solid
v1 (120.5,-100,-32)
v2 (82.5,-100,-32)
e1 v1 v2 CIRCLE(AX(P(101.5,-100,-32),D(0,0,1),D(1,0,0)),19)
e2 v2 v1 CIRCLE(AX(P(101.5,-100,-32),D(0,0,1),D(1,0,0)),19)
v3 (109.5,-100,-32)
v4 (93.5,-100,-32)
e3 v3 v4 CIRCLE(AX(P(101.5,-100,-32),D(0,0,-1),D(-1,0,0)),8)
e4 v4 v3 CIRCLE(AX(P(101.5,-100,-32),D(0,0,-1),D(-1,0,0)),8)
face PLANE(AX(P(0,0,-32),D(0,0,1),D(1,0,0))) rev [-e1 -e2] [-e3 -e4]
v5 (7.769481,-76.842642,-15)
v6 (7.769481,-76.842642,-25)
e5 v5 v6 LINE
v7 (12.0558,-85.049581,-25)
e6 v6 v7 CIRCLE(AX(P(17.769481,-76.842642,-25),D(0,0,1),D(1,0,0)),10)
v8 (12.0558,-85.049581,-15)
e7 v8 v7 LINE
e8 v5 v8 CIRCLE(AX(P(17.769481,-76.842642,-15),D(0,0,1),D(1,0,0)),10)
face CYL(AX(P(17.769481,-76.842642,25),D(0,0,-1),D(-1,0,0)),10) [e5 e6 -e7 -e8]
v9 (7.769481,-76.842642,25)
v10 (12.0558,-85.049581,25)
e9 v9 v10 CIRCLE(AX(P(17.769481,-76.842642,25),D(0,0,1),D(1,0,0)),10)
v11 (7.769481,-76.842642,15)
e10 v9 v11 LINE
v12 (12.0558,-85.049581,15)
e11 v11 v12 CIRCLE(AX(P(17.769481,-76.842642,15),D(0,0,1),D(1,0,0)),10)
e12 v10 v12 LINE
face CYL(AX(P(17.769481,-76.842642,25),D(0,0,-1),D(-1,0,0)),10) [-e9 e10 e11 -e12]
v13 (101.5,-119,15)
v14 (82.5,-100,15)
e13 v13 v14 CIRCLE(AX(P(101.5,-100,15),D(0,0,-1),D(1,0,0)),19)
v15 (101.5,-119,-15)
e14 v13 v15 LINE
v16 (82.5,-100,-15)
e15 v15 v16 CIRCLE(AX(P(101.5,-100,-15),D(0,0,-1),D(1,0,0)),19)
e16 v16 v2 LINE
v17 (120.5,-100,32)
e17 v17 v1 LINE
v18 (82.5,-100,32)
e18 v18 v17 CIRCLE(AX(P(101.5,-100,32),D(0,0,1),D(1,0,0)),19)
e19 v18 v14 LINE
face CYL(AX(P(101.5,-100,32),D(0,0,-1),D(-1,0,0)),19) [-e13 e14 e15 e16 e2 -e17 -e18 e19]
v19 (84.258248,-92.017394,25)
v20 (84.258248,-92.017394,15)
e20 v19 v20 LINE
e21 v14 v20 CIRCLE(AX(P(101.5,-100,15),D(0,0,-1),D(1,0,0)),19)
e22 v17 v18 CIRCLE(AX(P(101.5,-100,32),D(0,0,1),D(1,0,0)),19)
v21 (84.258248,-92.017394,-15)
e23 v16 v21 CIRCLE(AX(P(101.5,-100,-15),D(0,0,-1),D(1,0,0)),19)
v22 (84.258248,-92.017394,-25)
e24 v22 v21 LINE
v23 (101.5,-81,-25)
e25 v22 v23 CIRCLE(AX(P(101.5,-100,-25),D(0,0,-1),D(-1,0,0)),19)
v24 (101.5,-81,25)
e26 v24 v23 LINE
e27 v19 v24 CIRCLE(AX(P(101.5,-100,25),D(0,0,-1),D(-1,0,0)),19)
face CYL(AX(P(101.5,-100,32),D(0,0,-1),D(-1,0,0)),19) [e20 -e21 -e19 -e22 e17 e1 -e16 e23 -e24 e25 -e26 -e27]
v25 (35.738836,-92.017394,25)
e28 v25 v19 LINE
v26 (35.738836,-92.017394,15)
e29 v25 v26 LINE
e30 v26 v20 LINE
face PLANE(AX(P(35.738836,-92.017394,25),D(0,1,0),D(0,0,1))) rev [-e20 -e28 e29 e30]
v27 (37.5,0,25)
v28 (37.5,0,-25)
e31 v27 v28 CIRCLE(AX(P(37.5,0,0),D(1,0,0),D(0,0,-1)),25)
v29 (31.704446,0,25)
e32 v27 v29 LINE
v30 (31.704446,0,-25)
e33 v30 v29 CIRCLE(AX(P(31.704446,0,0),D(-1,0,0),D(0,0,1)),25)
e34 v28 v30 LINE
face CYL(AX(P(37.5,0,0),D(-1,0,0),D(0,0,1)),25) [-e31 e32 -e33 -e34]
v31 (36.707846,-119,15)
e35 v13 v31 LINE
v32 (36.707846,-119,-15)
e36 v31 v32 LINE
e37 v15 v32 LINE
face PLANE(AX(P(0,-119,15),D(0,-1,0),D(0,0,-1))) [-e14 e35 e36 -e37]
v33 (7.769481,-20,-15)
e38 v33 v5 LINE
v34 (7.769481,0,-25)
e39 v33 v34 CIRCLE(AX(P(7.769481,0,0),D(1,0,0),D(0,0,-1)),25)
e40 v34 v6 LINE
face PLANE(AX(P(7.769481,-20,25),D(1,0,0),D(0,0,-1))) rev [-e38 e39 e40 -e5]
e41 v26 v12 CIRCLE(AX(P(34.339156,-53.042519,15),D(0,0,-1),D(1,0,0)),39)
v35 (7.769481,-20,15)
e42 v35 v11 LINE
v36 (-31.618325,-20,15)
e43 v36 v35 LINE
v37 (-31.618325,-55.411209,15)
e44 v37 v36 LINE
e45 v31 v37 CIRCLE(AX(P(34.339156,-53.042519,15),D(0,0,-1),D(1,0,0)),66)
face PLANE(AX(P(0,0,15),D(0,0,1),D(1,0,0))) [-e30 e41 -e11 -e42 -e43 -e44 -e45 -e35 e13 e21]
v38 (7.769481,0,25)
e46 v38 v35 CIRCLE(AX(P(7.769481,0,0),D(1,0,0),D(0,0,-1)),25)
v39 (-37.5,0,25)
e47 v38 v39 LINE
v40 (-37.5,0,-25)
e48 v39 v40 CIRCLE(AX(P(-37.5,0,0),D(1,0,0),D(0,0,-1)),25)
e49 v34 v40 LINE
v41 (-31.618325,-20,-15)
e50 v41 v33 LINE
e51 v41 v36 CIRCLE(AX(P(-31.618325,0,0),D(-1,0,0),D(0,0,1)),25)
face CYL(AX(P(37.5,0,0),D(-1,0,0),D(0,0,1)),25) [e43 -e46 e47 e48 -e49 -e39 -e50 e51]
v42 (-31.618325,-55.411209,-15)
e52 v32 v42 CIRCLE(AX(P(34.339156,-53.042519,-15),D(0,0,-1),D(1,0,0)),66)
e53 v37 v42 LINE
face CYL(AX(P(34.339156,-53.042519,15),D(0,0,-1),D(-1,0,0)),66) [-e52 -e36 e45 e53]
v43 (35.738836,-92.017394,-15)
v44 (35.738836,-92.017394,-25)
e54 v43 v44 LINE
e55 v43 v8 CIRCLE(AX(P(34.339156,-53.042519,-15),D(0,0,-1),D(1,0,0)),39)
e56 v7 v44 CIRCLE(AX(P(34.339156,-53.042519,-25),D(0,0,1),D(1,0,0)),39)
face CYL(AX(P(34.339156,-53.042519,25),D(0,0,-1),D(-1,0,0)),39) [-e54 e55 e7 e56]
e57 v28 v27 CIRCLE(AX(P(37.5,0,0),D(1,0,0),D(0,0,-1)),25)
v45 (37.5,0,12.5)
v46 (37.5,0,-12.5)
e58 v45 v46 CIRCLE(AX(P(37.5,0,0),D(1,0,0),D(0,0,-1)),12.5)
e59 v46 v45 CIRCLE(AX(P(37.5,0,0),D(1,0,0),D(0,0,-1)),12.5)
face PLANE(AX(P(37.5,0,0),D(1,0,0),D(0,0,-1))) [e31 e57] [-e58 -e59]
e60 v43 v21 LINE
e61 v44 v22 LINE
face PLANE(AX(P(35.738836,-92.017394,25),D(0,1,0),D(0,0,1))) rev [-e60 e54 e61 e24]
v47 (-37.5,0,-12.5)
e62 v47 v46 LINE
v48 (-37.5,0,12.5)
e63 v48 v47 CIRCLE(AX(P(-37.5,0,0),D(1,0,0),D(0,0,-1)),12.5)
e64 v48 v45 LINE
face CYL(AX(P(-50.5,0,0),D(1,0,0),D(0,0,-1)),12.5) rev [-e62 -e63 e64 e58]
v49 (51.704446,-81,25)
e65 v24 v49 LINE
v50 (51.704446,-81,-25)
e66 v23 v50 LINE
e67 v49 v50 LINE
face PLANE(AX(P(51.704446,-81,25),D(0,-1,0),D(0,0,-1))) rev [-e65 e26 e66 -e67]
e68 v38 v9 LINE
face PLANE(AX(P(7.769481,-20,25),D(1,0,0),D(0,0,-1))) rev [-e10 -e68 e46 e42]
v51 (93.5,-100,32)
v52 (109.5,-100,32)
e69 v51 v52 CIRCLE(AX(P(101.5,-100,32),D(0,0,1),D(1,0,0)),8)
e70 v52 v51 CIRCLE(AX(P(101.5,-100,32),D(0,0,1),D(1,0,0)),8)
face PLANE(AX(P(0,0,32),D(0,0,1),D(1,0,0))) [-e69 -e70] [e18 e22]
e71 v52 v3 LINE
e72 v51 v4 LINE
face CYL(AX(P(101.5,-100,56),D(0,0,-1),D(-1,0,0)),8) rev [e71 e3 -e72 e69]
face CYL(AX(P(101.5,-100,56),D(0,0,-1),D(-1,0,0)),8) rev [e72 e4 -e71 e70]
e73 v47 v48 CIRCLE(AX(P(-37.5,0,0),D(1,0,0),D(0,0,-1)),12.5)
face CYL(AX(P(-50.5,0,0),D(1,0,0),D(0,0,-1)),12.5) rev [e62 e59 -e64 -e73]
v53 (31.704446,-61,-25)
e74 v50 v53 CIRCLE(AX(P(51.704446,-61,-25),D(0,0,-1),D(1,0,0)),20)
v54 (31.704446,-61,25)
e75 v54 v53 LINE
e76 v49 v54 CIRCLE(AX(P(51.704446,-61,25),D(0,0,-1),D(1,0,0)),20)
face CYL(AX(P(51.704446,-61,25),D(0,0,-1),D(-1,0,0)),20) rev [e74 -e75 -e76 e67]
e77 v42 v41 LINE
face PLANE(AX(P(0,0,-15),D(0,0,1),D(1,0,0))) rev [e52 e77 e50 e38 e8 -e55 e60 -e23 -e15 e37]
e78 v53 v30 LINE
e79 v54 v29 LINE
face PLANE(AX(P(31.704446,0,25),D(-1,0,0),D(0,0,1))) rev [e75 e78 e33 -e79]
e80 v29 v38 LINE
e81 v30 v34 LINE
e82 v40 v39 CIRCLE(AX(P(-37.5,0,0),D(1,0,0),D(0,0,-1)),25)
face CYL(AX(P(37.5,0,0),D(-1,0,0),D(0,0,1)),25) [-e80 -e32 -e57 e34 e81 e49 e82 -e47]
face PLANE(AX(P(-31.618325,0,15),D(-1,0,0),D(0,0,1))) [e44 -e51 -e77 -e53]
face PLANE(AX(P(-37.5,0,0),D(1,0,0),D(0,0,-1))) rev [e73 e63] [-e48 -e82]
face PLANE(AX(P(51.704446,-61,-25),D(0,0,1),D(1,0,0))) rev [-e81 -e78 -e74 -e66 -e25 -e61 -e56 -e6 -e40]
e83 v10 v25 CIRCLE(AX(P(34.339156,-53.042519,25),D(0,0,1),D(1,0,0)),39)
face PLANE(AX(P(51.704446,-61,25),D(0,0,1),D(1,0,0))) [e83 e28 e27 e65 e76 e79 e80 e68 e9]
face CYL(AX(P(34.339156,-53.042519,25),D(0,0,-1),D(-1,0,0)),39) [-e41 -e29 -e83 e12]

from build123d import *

# Parameters (mm, degrees)
HUB_1_PROFILE_R       = 25
HUB_1_BOSS_75MM_DEPTH = 37.5
HUB_2_PROFILE_R       = 19
HUB_2_BOSS_64MM_DEPTH = 32
CURVED_ARM_WEB_DEPTH  = 15
ARM_FLANGE_DEPTH      = 25
HUB_1_BORE_PROFILE_R  = 12.5
HUB_1_BORE_DEPTH      = 88
HUB_2_BORE_PROFILE_R  = 8
HUB_2_BORE_DEPTH      = 88


with BuildPart() as part:
    # Hub 1 Profile → Hub 1 Boss 75mm (new, symmetric)
    with BuildSketch(Plane(origin=(0, 0, 0), x_dir=(0, 0, -1), z_dir=(1, 0, 0))):
        Circle(HUB_1_PROFILE_R)
    extrude(amount=HUB_1_BOSS_75MM_DEPTH, both=True)



with BuildPart() as body_2:
    # Hub 2 Profile → Hub 2 Boss 64mm (new, symmetric)
    with BuildSketch(Plane.XY):
        with Locations((101.5, -100)):
            Circle(HUB_2_PROFILE_R)
    extrude(amount=HUB_2_BOSS_64MM_DEPTH, both=True)


with BuildPart() as part_1:
    add(part.part)

    add(body_2.part)  # Curved Arm Web merges body 2
    # Curved Arm Profile → Curved Arm Web (add, symmetric)
    with BuildSketch(Plane.XY):
        with BuildLine():
            Line((36.70784585, -119), (101.5, -119))
            ThreePointArc((101.5, -119), (85.489542295, -110.23060331), (84.258248254, -92.017394113))
            Line((84.258248254, -92.017394113), (35.73883627, -92.017394113))
            ThreePointArc((35.73883627, -92.017394113), (23.331450339, -90.456826651), (12.055799796, -85.049581394))
            ThreePointArc((12.055799796, -85.049581394), (8.905598759, -81.472069365), (7.769480814, -76.842642304))
            Line((7.769480814, -76.842642304), (7.769480814, -18.704046106))
            Line((7.769480814, -18.704046106), (-31.61832529, -18.704046106))
            Line((-31.61832529, -18.704046106), (-31.61832529, -25))
            Line((-31.61832529, -25), (-31.61832529, -55.411209028))
            ThreePointArc((-31.61832529, -55.411209028), (-10.624909538, -101.356417889), (36.70784585, -119))
        make_face()
    extrude(amount=CURVED_ARM_WEB_DEPTH, both=True)

    # Arm Flange Profile → Arm Flange (add, symmetric)
    with BuildSketch(Plane.XY):
        with BuildLine():
            Line((31.704445688, -20), (31.704445688, -61))
            ThreePointArc((31.704445688, -61), (37.562310065, -75.142135624), (51.704445688, -81))
            Line((51.704445688, -81), (101.5, -81))
            ThreePointArc((101.5, -81), (91.26939669, -83.989542295), (84.258248254, -92.017394113))
            Line((84.258248254, -92.017394113), (35.73883627, -92.017394113))
            ThreePointArc((35.73883627, -92.017394113), (23.331450339, -90.456826651), (12.055799796, -85.049581394))
            ThreePointArc((12.055799796, -85.049581394), (8.905598759, -81.472069365), (7.769480814, -76.842642304))
            Line((7.769480814, -76.842642304), (7.769480814, -20))
            Line((7.769480814, -20), (7.769480814, 0))
            Line((7.769480814, 0), (31.704445688, 0))
            Line((31.704445688, 0), (31.704445688, -20))
        make_face()
    extrude(amount=ARM_FLANGE_DEPTH, both=True)

    # Hub 1 Bore Profile → Hub 1 Bore (cut)
    with BuildSketch(Plane(origin=(37.5, 0, 0), x_dir=(0, 0, -1), z_dir=(1, 0, 0))):
        Circle(HUB_1_BORE_PROFILE_R)
    extrude(amount=-HUB_1_BORE_DEPTH, mode=Mode.SUBTRACT)

    # Hub 2 Bore Profile → Hub 2 Bore (cut)
    with BuildSketch(Plane(origin=(0, 0, -32), x_dir=(-1, 0, 0), z_dir=(0, 0, -1))):
        with Locations((-101.5, -100)):
            Circle(HUB_2_BORE_PROFILE_R)
    extrude(amount=-HUB_2_BORE_DEPTH, mode=Mode.SUBTRACT)


solid = part_1.part
